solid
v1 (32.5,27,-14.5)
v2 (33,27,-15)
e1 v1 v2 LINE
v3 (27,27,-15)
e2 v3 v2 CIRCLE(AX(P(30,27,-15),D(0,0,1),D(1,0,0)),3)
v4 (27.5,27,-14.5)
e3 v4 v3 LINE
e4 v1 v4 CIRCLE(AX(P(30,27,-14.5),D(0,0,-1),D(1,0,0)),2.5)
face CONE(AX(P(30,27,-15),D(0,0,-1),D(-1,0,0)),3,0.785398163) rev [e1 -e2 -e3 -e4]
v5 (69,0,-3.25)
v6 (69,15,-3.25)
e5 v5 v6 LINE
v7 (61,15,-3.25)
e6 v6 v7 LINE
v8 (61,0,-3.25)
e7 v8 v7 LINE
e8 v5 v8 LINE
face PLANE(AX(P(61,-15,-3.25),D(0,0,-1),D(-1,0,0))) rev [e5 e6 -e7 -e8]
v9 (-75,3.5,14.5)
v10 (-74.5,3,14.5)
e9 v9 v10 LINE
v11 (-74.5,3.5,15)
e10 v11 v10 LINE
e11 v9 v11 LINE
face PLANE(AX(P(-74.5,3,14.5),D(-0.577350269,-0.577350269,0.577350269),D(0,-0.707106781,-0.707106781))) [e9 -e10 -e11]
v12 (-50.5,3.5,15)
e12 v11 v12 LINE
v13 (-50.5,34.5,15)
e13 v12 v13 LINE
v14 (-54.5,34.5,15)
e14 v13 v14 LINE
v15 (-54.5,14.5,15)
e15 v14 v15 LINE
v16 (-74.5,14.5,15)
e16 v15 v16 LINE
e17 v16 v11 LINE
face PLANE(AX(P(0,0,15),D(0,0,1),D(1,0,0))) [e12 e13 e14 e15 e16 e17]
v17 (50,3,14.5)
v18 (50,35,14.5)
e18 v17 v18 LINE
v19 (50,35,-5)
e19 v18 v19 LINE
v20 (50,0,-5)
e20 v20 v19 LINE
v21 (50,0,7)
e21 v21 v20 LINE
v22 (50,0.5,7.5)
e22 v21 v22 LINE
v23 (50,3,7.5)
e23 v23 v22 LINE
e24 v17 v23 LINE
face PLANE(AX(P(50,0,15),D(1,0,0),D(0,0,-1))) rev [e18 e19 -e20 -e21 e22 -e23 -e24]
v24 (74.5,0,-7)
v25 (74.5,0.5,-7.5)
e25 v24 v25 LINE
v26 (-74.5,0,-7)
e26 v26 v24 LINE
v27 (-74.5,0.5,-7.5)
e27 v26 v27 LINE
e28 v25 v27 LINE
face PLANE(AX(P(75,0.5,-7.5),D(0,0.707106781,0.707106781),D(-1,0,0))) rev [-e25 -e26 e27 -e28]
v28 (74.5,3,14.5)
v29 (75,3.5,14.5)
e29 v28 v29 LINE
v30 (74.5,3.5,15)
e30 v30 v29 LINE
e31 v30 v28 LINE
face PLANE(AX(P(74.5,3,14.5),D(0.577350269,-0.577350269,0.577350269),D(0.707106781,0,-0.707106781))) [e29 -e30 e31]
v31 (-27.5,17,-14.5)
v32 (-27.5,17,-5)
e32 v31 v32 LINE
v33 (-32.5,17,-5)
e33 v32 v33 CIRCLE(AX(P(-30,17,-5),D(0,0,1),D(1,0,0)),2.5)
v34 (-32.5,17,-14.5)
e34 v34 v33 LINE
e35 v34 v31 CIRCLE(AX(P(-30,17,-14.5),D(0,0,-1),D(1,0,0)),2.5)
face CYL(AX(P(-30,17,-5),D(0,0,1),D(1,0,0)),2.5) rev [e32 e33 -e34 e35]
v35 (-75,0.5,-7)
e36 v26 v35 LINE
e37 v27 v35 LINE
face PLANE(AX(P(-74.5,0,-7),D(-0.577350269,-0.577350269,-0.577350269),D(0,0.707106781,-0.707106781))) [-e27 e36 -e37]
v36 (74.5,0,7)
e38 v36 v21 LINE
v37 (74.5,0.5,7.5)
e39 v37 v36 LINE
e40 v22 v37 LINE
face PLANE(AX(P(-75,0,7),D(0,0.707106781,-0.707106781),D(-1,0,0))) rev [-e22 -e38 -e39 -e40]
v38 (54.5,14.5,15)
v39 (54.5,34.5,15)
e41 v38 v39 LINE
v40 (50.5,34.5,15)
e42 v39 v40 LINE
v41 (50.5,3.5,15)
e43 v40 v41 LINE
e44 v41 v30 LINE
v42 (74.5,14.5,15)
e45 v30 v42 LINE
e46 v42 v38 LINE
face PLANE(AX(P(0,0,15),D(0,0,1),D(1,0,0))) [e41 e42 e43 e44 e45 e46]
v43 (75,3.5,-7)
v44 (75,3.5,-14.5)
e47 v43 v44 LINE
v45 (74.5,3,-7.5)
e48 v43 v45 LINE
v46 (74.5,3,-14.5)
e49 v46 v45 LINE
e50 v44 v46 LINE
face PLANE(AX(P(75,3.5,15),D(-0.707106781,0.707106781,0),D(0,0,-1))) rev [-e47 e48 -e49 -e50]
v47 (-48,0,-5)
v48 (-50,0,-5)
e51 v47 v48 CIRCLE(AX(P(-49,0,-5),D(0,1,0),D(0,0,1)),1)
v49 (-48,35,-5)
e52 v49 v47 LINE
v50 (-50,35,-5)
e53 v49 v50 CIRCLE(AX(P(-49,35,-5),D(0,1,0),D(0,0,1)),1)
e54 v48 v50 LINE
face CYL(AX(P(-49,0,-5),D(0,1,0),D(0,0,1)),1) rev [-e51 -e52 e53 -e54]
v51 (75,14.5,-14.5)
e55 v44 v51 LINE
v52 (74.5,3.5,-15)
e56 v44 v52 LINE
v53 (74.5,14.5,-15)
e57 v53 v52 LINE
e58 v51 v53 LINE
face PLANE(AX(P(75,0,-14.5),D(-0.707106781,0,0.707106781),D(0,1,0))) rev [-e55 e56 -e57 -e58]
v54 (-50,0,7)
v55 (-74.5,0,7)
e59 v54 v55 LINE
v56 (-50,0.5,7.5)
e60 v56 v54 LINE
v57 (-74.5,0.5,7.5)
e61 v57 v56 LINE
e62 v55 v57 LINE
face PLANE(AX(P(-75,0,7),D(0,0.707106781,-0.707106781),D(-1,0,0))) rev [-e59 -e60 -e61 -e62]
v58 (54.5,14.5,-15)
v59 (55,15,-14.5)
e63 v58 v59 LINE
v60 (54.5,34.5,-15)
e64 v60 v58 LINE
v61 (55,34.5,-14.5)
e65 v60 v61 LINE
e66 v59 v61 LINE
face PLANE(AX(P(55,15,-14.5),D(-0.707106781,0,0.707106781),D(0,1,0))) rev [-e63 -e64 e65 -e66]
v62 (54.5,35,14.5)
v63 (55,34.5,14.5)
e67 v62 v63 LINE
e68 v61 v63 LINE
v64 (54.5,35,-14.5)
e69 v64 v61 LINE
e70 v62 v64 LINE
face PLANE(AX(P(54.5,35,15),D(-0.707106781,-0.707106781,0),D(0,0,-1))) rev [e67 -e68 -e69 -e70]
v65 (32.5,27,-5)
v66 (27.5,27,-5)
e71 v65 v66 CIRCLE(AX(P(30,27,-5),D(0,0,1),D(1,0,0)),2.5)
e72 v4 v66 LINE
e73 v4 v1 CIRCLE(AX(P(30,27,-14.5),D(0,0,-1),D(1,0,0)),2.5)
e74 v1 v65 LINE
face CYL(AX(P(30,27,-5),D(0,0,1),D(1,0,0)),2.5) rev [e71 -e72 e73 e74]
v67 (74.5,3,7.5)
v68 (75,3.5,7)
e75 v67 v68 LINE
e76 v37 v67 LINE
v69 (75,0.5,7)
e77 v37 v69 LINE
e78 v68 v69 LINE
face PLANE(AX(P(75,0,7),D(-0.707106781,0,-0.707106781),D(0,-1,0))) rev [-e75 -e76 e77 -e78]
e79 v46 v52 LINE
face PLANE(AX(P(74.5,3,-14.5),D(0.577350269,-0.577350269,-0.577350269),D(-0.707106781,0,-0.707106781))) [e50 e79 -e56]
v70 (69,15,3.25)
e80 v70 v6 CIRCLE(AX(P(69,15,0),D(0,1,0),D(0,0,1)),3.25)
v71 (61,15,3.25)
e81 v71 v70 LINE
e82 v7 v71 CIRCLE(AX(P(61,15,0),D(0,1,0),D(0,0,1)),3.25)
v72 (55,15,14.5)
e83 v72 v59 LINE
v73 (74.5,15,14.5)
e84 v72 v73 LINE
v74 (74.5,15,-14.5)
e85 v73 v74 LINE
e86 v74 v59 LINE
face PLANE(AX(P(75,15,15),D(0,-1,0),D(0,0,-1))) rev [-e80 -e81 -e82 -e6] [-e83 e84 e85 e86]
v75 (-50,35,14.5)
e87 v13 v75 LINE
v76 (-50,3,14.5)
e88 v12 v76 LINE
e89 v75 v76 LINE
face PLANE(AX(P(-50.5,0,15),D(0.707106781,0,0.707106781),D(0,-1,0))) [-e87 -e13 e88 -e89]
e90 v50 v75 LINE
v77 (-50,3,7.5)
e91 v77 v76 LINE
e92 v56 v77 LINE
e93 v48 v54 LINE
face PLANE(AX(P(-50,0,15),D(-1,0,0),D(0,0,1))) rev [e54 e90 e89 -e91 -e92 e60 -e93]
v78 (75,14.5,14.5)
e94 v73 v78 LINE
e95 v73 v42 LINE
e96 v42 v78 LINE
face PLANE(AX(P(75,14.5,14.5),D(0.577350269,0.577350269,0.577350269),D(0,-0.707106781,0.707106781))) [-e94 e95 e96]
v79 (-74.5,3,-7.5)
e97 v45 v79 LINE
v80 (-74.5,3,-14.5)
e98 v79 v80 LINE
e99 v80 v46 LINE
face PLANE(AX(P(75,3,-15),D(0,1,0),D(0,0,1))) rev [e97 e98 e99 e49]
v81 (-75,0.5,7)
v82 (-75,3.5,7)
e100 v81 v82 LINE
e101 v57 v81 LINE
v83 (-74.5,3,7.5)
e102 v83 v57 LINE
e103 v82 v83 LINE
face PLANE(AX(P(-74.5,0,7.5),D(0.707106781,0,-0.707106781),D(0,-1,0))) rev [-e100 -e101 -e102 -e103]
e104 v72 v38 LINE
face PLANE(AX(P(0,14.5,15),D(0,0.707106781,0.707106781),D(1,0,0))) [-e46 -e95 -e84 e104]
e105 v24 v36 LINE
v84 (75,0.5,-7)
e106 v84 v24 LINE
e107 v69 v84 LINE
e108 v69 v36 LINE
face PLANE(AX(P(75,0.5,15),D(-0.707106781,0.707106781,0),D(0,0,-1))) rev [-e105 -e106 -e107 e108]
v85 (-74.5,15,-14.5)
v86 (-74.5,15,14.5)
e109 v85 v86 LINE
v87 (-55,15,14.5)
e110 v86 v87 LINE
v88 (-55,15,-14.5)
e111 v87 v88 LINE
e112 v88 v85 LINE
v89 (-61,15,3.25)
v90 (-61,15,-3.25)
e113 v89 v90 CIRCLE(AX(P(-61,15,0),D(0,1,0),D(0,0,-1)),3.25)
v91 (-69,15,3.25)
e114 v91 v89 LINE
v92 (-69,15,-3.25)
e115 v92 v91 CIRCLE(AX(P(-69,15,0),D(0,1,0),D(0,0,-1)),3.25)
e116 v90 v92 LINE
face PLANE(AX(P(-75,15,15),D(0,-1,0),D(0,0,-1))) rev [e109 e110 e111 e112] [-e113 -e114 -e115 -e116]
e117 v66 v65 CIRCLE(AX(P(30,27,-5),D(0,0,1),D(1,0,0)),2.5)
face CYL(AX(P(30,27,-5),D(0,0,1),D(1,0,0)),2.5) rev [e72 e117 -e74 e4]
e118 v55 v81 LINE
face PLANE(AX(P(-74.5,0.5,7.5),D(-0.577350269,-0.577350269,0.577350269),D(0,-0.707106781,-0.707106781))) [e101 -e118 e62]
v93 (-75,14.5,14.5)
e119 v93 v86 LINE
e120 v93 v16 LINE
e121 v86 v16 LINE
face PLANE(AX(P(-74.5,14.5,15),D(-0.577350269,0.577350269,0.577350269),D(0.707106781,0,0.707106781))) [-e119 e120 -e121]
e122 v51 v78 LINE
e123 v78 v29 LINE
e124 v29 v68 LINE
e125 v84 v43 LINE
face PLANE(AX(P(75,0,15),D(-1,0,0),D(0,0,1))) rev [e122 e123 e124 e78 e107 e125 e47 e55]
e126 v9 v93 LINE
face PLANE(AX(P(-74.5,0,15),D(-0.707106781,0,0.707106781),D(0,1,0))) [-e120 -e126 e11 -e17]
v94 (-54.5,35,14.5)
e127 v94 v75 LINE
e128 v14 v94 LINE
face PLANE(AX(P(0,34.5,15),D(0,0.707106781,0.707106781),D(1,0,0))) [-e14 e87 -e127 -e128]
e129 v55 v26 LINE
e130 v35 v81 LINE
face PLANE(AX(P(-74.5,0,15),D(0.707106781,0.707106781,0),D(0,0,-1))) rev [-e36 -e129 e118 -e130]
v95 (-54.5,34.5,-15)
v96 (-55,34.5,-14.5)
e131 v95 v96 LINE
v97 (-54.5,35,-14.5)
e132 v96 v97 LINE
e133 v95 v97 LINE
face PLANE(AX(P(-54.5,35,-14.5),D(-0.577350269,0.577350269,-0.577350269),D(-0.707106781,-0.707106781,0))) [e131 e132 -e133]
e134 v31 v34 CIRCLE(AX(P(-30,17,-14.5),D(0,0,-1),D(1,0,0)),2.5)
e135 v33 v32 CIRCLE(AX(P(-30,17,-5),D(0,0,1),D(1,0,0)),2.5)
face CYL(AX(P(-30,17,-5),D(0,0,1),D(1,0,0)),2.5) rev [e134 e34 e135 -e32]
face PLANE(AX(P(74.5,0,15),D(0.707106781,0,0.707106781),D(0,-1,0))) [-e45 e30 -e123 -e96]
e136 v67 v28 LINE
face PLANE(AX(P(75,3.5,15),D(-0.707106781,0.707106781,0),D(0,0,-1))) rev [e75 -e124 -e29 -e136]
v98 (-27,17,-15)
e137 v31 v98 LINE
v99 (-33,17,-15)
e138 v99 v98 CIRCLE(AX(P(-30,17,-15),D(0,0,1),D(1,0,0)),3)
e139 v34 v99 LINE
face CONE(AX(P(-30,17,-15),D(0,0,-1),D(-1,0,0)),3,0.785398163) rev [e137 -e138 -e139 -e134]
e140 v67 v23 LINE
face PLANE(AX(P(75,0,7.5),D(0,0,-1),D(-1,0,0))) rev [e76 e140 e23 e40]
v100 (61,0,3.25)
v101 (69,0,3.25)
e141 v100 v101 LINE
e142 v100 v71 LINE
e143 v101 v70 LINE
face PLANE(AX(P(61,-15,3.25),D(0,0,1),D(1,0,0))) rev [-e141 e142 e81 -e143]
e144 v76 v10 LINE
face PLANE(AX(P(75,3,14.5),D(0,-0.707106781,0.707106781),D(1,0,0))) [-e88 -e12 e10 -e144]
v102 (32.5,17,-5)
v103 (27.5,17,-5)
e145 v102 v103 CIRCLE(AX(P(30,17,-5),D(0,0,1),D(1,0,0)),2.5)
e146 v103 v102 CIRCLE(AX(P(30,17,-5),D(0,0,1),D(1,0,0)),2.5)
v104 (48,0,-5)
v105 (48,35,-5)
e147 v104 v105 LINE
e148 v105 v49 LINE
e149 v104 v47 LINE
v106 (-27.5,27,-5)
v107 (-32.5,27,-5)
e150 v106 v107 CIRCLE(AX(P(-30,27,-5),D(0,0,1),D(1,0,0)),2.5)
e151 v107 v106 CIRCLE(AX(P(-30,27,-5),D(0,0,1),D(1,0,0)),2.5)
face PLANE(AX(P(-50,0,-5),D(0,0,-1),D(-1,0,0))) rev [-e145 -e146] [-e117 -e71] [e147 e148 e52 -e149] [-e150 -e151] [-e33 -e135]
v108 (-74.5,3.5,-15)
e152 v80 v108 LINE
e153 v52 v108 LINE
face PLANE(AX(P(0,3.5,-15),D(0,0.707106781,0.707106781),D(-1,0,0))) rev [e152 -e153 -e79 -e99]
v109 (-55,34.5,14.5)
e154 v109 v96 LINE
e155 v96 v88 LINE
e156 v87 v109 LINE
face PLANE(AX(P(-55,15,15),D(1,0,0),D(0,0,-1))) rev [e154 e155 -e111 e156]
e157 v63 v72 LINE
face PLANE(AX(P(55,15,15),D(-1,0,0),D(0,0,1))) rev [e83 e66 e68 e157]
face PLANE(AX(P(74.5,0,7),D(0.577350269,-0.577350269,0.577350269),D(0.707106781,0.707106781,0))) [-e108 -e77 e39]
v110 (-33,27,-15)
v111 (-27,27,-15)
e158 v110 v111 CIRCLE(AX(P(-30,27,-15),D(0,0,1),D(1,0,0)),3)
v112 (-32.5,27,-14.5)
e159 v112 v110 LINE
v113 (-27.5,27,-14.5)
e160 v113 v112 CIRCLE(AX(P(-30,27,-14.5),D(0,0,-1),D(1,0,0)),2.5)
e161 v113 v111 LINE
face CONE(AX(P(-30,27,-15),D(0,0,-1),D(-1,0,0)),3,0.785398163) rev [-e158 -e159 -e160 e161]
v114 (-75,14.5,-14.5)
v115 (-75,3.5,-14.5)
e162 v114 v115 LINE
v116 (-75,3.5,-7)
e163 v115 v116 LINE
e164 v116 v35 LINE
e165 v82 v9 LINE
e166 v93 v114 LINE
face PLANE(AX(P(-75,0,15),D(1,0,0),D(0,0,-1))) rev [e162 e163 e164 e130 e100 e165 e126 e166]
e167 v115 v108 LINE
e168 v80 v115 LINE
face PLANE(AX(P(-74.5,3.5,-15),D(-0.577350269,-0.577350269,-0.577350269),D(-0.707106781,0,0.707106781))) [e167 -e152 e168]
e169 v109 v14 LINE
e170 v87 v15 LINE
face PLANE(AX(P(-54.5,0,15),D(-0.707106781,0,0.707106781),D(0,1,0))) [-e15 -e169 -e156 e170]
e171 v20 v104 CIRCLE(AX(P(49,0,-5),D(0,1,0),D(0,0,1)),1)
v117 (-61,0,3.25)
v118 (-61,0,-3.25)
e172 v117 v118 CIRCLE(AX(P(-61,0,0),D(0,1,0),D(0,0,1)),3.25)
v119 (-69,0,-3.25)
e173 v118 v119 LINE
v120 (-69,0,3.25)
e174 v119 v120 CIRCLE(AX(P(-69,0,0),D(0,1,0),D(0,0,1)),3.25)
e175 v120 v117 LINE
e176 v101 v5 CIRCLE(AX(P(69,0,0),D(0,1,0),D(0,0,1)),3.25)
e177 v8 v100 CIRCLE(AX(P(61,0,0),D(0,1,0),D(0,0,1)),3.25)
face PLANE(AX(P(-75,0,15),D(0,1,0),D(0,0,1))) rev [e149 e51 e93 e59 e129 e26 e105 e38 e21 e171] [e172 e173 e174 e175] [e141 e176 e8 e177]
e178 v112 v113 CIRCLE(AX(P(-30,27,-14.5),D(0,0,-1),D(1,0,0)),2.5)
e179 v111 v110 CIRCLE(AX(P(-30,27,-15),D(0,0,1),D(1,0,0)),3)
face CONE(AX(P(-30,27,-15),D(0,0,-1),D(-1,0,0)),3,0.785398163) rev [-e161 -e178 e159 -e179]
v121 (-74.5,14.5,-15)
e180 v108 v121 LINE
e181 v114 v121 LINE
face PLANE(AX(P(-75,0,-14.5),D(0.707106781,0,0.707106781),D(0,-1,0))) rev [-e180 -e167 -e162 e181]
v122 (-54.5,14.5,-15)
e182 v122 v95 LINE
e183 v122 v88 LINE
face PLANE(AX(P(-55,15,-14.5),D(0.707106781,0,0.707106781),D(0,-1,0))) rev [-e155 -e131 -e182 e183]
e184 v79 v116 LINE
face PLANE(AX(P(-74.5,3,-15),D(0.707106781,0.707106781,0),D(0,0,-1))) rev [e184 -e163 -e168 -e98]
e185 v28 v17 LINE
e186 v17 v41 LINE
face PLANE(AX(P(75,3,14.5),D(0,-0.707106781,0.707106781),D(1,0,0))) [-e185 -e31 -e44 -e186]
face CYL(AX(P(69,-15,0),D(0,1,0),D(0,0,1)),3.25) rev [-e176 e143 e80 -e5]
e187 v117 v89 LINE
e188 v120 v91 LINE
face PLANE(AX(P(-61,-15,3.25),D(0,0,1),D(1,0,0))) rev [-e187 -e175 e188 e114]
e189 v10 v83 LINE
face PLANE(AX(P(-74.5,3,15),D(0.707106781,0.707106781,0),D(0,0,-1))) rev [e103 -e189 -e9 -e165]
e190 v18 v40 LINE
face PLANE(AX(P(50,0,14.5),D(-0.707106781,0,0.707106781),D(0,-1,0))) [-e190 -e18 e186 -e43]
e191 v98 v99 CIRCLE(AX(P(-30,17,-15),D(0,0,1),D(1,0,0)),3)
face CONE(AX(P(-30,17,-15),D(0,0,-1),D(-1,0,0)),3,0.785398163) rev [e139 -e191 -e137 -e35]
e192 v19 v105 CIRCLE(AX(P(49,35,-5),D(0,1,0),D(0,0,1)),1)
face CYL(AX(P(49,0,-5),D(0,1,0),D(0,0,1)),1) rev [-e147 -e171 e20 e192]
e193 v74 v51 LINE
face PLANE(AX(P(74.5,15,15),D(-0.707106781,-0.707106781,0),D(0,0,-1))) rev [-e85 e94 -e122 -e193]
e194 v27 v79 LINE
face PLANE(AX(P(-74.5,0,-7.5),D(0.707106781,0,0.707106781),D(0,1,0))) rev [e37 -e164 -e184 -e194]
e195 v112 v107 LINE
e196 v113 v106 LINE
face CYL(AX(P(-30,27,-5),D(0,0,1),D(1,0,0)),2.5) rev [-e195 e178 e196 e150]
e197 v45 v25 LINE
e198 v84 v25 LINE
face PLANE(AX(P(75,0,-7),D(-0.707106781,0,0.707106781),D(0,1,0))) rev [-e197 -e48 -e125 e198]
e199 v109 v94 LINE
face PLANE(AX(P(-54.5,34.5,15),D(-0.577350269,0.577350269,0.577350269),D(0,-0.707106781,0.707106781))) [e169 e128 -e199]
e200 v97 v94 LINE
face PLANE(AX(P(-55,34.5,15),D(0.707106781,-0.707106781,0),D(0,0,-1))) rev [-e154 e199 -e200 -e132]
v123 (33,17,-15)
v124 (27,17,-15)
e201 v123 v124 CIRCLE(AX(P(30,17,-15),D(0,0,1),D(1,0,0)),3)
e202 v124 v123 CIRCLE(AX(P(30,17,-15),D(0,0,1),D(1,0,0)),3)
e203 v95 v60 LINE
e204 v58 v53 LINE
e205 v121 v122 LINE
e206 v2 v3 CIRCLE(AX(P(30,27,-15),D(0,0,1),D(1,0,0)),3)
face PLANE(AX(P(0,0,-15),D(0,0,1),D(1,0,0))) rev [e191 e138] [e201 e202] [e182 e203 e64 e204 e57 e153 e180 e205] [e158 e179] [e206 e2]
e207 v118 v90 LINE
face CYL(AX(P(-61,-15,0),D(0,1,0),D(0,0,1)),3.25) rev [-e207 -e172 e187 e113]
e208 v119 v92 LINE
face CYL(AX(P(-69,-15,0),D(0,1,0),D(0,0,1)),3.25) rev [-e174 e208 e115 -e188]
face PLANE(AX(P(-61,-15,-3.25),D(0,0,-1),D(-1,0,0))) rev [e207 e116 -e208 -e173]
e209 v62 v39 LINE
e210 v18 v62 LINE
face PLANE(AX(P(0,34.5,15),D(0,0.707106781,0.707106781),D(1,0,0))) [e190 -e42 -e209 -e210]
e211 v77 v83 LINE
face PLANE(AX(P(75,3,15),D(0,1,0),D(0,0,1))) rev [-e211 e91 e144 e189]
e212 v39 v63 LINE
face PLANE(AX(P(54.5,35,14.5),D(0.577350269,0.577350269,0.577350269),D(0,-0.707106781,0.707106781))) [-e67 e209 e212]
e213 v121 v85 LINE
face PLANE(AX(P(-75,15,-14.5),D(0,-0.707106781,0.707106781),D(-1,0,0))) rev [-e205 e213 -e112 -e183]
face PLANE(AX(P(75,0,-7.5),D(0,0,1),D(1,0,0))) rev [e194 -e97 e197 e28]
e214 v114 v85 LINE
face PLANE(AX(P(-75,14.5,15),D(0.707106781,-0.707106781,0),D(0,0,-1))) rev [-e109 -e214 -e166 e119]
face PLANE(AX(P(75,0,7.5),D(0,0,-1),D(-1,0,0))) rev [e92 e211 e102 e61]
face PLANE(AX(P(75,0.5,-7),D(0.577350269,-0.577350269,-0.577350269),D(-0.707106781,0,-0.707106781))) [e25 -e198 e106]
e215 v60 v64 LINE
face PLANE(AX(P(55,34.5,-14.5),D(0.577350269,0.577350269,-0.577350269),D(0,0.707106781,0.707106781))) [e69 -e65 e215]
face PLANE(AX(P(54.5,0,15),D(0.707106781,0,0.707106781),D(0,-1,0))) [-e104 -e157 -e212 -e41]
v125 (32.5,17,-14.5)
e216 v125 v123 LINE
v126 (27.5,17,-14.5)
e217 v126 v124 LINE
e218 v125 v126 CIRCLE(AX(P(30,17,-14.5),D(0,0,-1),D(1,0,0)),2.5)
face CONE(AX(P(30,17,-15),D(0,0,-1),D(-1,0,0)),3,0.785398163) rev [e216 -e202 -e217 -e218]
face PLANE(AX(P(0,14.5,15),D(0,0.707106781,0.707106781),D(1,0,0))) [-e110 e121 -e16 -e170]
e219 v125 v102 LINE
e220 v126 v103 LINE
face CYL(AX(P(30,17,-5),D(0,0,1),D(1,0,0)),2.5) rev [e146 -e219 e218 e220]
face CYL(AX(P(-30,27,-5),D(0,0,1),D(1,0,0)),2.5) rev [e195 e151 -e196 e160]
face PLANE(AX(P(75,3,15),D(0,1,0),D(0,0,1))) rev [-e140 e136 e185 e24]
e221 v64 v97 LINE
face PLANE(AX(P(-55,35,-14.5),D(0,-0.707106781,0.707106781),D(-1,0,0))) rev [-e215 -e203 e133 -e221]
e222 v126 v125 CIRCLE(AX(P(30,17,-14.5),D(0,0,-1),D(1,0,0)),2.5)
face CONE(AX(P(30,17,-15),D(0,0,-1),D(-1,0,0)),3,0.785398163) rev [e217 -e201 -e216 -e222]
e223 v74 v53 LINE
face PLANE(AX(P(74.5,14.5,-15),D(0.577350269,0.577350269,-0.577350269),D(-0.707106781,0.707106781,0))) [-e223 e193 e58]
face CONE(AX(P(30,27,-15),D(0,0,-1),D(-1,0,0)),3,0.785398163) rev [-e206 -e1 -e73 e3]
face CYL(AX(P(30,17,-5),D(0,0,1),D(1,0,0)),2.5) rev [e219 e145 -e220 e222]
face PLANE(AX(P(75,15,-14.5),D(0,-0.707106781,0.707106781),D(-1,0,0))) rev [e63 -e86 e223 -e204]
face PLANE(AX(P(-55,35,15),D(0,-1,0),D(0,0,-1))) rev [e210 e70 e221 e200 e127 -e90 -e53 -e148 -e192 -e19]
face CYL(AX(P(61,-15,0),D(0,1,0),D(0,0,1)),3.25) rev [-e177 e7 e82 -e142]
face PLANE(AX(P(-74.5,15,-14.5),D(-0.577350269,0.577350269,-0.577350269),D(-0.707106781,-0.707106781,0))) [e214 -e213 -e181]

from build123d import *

# Parameters (mm, degrees)
EXTRUDE_1_DEPTH        = 15
SKETCH_2_W             = 7.5
SKETCH_2_H             = 3
CUT_EXTRUDE_1_DEPTH    = 155.757875405
SKETCH_3_W             = 100
SKETCH_3_H             = 20
CUT_EXTRUDE_2_DEPTH    = 85.113019206
CUT_EXTRUDE_3_DEPTH    = 30
HOLE_WIZARD_M6_1_D     = 5
PATTERN_LINEAR_1_COUNT = 2
PATTERN_LINEAR_1_PITCH = 10
CHAMFER_1_SIZE         = 0.5
SKETCH_7_R             = 1
CUT_EXTRUDE_4_DEPTH    = 85.113019206


with BuildPart() as part:
    # 草图1 → 凸台-拉伸1 (new, symmetric)
    with BuildSketch(Plane.XY):
        Polygon((-75, 0), (-75, 15), (-55, 15), (-55, 35), (55, 35), (55, 15), (75, 15), (75, 0), align=None)
    extrude(amount=EXTRUDE_1_DEPTH, both=True)

    # 草图2 → 切除-拉伸1 (cut, through all)
    with BuildSketch(Plane.ZY.offset(75)):
        with Locations((-11.25, 1.5)):
            Rectangle(SKETCH_2_W, SKETCH_2_H)
        with Locations((11.25, 1.5)):
            Rectangle(SKETCH_2_W, SKETCH_2_H)
    extrude(amount=-CUT_EXTRUDE_1_DEPTH, mode=Mode.SUBTRACT)

    # 草图3 → 切除-拉伸2 (cut, through all)
    with BuildSketch(Plane(origin=(0, 35, 0), x_dir=(1, 0, 0), z_dir=(0, 1, 0))):
        with Locations((0, -5)):
            Rectangle(SKETCH_3_W, SKETCH_3_H)
    extrude(amount=-CUT_EXTRUDE_2_DEPTH, mode=Mode.SUBTRACT)

    # 草图4 → 切除-拉伸3 (cut)
    with BuildSketch(Plane(origin=(0, 15, 0), x_dir=(1, 0, 0), z_dir=(0, 1, 0))):
        with BuildLine():
            Line((61, 3.25), (69, 3.25))
            ThreePointArc((69, 3.25), (72.25, 0), (69, -3.25))
            Line((69, -3.25), (61, -3.25))
            ThreePointArc((61, -3.25), (57.75, 0), (61, 3.25))
        make_face()
        with BuildLine():
            Line((-61, 3.25), (-69, 3.25))
            ThreePointArc((-69, 3.25), (-72.25, 0), (-69, -3.25))
            Line((-69, -3.25), (-61, -3.25))
            ThreePointArc((-61, -3.25), (-57.75, 0), (-61, 3.25))
        make_face()
    extrude(amount=-CUT_EXTRUDE_3_DEPTH, mode=Mode.SUBTRACT)

    # M6 螺纹孔1 (through all)
    with Locations(Plane.XY.offset(-5)):
        with Locations((-30, 17), (30, 17)):
            hole_wizard_m6_1 = Hole(HOLE_WIZARD_M6_1_D / 2)

    # 阵列(线性)1: M6 螺纹孔1 ×2
    with Locations(*[(0, i * PATTERN_LINEAR_1_PITCH, 0) for i in range(1, PATTERN_LINEAR_1_COUNT)]):
        add(hole_wizard_m6_1, mode=Mode.SUBTRACT)

    # 倒角1
    chamfer_1_edges = [part.edges().sort_by_distance(p)[0] for p in [
        (55, 25, -15),
        (65, 15, -15),
        (32.5, 17, -15),
        (-27.5, 17, -15),
        (32.5, 27, -15),
        (65, 15, 15),
        (-27.5, 27, -15),
        (-75, 15, 0),
        (-55, 35, 0),
        (55, 35, 0),
        (75, 15, 0),
        (55, 25, 15),
        (52.5, 35, 15),
        (75, 9, -15),
        (-55, 25, 15),
        (75, 9, 15),
        (-75, 0, 0),
        (-65, 15, 15),
        (75, 0, 0),
        (75, 3, -11.25),
        (-75, 9, 15),
        (0, 3, -15),
        (75, 1.5, -7.5),
        (0, 0, -7.5),
        (-75, 1.5, -7.5),
        (-75, 3, -11.25),
        (75, 1.5, 7.5),
        (62.5, 0, 7.5),
        (75, 3, 11.25),
        (62.5, 3, 15),
        (-75, 3, 11.25),
        (-75, 1.5, 7.5),
        (-62.5, 3, 15),
        (-62.5, 0, 7.5),
        (-52.5, 35, 15),
        (-50, 19, 15),
        (50, 19, 15),
        (-75, 9, -15),
        (-65, 15, -15),
        (-55, 25, -15),
        (0, 35, -15),
    ]]
    chamfer(chamfer_1_edges, length=CHAMFER_1_SIZE)

    # 草图7 → 切除-拉伸4 (cut, through all)
    with BuildSketch(Plane(origin=(0, 35, 0), x_dir=(1, 0, 0), z_dir=(0, 1, 0))):
        with Locations((-49, 5)):
            Circle(SKETCH_7_R)
        with Locations((49, 5)):
            Circle(SKETCH_7_R)
    extrude(amount=-CUT_EXTRUDE_4_DEPTH, mode=Mode.SUBTRACT)


solid = part.part
